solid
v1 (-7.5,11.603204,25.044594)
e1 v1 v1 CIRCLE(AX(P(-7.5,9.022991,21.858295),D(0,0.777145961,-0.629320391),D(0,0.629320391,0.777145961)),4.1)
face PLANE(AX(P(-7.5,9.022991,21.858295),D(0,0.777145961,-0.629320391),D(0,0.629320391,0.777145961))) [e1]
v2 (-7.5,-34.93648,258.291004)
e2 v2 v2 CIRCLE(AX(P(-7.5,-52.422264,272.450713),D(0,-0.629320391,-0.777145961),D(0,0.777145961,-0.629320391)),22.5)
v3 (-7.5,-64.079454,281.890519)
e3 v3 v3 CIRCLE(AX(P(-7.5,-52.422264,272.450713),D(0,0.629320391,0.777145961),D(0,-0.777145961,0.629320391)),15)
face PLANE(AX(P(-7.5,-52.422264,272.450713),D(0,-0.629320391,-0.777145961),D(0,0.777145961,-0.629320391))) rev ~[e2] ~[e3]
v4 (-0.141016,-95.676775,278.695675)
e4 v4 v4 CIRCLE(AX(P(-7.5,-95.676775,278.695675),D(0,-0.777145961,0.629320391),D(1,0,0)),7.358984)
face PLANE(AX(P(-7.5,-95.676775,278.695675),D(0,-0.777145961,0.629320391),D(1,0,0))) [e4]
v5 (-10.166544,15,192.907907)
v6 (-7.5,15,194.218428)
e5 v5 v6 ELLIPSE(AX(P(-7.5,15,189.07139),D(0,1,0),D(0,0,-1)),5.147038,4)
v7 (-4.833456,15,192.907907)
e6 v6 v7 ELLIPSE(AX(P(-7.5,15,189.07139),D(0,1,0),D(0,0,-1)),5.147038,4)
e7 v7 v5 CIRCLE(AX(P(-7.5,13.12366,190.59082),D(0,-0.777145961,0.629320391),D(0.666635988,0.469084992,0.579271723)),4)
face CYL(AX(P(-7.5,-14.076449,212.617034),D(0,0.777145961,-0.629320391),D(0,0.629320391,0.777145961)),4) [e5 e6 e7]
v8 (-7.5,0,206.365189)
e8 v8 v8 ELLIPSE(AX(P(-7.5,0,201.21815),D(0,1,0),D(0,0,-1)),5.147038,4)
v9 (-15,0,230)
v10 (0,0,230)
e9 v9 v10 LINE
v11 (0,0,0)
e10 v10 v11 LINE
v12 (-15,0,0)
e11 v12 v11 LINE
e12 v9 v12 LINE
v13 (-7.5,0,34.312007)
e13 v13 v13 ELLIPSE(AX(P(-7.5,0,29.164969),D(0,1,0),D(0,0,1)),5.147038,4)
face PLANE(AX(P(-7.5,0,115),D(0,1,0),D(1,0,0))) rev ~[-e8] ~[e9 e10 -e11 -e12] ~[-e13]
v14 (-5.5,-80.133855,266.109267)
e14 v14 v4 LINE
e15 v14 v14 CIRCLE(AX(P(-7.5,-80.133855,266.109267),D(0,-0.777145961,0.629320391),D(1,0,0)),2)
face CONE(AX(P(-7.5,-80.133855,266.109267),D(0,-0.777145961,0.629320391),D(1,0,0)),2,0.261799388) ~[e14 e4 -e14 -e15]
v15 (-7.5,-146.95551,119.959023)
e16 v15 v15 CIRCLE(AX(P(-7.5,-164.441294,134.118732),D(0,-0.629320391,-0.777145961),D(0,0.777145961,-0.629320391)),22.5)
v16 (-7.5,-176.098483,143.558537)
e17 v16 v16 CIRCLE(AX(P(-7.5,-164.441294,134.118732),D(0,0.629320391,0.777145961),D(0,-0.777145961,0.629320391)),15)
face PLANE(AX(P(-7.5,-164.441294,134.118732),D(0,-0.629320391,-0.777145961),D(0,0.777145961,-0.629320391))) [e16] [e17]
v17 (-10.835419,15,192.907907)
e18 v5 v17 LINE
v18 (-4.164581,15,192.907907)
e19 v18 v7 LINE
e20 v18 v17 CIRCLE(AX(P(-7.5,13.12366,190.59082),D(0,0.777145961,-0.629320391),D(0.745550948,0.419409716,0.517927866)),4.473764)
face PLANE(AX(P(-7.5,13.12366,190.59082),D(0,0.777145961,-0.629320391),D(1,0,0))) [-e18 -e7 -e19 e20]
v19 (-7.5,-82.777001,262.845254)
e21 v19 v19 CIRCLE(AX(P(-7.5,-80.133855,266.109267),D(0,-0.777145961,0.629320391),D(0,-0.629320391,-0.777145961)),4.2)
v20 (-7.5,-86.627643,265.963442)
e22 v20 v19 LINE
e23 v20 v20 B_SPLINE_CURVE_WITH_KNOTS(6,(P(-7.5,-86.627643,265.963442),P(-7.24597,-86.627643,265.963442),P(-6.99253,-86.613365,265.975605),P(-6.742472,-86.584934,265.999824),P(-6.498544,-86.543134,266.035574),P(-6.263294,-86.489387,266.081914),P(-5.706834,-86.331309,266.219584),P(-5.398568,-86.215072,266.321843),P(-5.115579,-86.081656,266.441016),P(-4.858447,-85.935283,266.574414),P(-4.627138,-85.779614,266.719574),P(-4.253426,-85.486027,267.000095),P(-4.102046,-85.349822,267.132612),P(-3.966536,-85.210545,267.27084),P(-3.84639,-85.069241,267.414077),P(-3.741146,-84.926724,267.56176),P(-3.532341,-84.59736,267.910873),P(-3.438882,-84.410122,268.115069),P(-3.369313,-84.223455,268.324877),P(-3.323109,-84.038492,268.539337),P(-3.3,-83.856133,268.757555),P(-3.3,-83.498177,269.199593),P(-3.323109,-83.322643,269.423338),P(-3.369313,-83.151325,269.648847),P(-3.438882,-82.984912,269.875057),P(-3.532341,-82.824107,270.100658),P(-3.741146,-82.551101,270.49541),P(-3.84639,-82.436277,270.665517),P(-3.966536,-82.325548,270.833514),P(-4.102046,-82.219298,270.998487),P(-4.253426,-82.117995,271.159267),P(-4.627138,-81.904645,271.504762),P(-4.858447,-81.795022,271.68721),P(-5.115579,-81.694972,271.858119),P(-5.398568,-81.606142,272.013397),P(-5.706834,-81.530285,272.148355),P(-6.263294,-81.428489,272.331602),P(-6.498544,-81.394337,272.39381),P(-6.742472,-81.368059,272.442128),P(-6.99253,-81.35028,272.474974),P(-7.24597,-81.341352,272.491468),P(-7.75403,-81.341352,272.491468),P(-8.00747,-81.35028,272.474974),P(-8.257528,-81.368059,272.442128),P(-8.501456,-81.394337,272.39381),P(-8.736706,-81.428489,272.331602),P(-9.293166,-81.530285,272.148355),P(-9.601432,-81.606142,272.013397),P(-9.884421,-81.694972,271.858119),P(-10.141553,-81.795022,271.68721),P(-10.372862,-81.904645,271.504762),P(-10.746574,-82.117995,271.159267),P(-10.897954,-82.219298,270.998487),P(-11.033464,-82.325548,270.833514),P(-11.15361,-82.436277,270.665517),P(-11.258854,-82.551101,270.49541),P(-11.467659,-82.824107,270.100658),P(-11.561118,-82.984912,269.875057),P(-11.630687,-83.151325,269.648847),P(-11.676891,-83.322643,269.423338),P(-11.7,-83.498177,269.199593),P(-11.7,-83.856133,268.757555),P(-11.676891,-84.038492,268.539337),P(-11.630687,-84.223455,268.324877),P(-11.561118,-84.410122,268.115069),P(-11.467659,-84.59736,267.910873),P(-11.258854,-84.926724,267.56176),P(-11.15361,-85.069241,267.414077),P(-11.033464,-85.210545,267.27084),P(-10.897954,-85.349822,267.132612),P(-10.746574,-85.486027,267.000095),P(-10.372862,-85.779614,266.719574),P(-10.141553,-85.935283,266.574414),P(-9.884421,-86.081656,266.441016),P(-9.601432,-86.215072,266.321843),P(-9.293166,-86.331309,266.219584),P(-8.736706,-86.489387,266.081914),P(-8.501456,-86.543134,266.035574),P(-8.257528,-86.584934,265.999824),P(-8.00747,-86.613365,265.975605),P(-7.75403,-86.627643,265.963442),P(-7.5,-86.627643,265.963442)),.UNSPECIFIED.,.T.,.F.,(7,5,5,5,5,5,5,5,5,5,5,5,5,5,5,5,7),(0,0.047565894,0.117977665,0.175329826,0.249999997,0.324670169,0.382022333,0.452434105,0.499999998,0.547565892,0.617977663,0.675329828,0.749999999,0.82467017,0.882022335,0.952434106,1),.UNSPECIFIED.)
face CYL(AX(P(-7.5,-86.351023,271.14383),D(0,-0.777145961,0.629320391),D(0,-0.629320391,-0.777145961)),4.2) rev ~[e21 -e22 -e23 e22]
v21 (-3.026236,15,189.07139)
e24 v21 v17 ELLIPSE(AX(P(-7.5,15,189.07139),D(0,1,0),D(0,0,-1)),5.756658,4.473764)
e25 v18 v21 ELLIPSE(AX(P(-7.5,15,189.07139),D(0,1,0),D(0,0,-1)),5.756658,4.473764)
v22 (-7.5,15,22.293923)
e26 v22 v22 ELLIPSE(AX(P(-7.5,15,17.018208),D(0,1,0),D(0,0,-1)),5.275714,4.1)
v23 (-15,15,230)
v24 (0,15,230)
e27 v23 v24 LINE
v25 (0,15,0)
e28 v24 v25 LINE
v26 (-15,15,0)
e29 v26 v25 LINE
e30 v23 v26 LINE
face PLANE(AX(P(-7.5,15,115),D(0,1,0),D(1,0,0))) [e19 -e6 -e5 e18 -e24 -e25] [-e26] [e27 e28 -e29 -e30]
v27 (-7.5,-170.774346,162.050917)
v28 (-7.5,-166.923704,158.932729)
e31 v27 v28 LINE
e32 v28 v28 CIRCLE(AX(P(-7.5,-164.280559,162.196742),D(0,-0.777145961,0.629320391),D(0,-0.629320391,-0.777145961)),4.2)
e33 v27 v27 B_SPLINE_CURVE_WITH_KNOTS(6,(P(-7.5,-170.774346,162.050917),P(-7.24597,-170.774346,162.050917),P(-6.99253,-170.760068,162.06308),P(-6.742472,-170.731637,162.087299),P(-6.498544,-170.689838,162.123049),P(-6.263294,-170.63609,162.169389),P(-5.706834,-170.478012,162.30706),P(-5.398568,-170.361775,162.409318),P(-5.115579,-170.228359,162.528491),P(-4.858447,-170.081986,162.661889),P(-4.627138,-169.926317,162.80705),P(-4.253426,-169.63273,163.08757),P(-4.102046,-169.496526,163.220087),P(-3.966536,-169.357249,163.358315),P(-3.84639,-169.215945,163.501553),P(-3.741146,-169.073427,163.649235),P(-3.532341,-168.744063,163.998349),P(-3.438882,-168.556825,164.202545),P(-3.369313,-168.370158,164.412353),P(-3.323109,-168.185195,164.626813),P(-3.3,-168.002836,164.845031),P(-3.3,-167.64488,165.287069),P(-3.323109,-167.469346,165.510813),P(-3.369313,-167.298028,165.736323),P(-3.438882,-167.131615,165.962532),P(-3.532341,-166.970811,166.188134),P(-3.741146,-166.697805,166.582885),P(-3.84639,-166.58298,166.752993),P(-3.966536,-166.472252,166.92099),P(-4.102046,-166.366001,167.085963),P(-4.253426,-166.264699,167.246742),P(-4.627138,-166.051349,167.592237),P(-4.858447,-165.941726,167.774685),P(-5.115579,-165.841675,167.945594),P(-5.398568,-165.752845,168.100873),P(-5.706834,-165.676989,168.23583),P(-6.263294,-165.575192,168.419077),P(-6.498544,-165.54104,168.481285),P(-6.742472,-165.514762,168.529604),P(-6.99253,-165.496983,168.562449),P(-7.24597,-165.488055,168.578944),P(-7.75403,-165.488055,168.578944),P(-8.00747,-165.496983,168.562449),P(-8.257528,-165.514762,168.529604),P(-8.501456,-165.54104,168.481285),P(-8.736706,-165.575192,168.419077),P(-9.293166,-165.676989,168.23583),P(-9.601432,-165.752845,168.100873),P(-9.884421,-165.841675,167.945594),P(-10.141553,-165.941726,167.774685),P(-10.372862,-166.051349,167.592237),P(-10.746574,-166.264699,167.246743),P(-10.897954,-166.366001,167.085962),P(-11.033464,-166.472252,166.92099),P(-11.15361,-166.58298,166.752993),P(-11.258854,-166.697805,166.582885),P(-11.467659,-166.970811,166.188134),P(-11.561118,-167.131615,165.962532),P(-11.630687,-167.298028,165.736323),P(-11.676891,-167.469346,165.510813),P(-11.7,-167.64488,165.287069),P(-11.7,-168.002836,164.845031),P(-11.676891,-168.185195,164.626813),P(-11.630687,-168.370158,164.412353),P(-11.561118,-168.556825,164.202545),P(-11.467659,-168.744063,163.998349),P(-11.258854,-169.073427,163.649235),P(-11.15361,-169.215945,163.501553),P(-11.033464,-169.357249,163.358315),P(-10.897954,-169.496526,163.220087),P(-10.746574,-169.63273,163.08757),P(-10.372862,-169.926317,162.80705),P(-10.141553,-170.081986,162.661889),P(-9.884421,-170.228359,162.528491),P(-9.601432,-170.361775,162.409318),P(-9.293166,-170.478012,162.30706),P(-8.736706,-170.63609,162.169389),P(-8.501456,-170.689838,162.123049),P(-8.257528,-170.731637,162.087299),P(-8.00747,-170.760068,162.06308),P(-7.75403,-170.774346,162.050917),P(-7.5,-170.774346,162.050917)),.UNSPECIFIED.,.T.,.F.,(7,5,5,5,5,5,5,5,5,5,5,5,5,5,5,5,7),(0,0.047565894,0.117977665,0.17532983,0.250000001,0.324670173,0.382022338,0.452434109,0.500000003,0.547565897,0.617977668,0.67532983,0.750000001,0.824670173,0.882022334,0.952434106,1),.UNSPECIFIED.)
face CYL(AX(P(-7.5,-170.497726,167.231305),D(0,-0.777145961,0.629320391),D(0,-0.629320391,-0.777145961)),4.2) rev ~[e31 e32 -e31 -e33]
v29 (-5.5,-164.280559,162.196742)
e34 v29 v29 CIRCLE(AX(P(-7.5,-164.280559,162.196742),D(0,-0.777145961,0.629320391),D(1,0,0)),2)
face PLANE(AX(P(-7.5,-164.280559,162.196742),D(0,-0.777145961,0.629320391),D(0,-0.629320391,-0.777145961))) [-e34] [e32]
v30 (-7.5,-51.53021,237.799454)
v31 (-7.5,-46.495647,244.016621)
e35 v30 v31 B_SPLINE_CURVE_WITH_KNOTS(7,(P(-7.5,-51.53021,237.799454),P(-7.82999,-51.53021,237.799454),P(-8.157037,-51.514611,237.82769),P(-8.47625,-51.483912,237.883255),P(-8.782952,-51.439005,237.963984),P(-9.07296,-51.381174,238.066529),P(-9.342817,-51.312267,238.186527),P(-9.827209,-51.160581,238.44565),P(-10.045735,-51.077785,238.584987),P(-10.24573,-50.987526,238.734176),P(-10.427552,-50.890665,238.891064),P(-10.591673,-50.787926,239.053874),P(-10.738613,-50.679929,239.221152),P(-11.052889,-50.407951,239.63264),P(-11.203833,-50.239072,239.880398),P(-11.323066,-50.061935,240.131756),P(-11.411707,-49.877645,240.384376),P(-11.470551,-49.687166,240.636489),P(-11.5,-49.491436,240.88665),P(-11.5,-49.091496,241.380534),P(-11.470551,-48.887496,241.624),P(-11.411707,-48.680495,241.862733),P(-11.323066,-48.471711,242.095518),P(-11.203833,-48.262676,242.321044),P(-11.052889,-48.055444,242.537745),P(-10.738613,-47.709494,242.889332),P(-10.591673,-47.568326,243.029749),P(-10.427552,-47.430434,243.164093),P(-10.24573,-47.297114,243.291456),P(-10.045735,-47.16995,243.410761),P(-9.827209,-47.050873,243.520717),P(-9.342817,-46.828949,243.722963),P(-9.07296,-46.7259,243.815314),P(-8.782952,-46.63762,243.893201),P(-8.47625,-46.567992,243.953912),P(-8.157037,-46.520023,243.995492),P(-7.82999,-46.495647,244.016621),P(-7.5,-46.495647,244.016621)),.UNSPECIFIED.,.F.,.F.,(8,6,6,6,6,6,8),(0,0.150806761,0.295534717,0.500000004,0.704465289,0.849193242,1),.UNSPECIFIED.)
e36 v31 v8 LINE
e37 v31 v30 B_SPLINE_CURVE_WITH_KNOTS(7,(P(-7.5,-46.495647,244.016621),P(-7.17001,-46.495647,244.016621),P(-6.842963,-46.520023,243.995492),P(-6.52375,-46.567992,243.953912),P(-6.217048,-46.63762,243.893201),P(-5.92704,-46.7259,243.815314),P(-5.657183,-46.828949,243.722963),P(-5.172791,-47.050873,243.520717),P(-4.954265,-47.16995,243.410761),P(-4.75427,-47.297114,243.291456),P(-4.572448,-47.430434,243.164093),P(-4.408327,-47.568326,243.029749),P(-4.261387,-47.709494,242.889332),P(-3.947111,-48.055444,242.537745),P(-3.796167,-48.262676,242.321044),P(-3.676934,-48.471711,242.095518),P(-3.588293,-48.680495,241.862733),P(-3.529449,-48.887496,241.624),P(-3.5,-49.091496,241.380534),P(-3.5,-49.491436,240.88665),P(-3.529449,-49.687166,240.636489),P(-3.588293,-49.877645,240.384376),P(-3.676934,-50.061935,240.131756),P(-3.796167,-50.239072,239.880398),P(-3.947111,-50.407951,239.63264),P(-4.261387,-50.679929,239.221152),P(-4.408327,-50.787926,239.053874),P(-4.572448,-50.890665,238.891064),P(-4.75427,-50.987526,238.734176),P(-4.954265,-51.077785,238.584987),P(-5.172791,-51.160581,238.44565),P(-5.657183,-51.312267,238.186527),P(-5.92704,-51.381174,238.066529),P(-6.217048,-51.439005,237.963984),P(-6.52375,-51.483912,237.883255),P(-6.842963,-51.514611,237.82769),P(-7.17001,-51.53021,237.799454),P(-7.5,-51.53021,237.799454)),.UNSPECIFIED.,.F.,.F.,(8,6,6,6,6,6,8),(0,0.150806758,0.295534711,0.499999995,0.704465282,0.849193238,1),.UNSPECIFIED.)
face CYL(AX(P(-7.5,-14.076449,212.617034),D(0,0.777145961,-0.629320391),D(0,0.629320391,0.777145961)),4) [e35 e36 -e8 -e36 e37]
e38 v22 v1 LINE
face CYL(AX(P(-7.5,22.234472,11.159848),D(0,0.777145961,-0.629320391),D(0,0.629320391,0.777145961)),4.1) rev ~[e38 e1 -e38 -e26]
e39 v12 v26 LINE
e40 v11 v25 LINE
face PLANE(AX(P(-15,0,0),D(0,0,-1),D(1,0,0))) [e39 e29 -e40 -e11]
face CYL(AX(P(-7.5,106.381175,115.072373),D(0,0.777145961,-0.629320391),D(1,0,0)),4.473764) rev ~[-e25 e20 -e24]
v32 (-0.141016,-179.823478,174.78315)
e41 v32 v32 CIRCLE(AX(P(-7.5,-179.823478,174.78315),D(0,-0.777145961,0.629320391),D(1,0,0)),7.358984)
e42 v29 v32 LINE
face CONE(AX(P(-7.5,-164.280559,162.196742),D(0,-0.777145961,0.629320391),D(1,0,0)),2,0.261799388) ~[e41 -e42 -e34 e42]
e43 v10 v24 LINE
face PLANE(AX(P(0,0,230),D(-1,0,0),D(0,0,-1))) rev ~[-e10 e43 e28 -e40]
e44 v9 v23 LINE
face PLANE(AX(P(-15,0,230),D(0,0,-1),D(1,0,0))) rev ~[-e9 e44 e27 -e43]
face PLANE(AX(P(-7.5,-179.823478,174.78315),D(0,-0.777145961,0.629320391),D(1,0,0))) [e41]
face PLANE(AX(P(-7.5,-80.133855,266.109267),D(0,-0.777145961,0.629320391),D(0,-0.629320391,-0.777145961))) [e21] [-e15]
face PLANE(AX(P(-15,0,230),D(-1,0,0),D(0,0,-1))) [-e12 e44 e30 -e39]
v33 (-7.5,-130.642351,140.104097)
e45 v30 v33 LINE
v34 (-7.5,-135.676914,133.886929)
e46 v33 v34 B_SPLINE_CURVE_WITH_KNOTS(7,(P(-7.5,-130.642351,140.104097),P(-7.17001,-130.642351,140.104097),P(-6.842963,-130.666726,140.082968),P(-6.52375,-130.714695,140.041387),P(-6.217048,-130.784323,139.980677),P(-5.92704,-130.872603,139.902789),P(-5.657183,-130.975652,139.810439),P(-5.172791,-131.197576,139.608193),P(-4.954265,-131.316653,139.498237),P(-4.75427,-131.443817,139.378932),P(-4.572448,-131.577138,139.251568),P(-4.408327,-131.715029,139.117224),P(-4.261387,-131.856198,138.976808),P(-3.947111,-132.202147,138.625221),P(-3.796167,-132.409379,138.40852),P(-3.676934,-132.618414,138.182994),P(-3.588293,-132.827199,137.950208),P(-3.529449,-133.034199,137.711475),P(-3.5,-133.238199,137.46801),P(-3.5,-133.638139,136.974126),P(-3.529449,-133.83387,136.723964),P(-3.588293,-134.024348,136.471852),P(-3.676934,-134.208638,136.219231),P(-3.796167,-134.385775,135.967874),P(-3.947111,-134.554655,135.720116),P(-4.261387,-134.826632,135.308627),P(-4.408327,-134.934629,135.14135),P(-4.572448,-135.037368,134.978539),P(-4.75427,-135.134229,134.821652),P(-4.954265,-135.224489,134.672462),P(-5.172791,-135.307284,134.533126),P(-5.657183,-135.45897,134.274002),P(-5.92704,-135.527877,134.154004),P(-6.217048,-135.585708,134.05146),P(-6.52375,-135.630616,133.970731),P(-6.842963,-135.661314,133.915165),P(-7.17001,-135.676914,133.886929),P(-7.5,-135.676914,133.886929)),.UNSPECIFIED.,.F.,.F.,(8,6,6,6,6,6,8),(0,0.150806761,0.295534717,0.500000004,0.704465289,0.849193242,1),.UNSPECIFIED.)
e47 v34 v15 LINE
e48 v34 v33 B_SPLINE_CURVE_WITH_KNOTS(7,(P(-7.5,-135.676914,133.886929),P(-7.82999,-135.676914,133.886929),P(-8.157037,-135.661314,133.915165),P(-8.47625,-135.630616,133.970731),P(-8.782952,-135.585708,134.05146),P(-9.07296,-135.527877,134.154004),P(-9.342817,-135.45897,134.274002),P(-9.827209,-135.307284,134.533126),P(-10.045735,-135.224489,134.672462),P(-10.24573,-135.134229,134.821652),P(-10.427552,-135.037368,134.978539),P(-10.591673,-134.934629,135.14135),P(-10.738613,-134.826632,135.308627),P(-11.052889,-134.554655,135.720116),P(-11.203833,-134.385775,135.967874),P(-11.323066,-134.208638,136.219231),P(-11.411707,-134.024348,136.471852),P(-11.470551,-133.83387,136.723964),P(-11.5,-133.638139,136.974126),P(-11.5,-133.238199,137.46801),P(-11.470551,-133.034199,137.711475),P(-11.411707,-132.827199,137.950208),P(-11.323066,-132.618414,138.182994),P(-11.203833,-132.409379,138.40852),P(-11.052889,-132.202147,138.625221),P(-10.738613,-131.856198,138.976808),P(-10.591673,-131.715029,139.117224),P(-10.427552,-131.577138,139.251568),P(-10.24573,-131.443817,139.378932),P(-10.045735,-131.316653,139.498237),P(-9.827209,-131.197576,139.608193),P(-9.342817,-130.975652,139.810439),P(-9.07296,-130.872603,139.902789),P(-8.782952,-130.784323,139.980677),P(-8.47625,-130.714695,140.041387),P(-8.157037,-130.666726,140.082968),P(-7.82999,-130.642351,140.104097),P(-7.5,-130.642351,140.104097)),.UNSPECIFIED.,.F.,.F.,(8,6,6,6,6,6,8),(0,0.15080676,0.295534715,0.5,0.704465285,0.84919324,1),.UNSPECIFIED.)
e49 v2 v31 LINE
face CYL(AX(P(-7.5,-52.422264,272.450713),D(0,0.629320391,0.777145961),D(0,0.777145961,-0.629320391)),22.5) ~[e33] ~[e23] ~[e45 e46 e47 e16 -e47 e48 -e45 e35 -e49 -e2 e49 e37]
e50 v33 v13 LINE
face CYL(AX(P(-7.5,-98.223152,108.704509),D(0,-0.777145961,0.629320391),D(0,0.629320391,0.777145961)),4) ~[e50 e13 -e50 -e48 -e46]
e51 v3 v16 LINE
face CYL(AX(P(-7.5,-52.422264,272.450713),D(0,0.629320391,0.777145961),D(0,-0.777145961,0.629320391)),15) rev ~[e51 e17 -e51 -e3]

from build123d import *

# Parameters (mm, degrees)
SKETCH2_W                     = 15
SKETCH2_H                     = 230
BOSS_EXTRUDE2_DEPTH           = 15
SKETCH4_R                     = 4
BOSS_EXTRUDE3_DEPTH           = 155
SKETCH5_R                     = 4.473763718
CUT_EXTRUDE1_DEPTH            = 120
SKETCH6_R                     = 4.1
CUT_EXTRUDE2_DEPTH            = 17
SKETCH7_R                     = 5.311376806
SKETCH7_R_2                   = 5.6699774
CUT_EXTRUDE3_DEPTH            = 62
SKETCH8_R                     = 22.5
BOSS_EXTRUDE4_DEPTH           = 178
SKETCH9_R                     = 4.2
CUT_EXTRUDE4_DEPTH            = 8
SKETCH10_R                    = 2
BOSS_EXTRUDE5_DEPTH           = 20
BOSS_EXTRUDE5_DRAFT           = -15
BOSS_EXTRUDE5_PROFILE_2_DEPTH = 20
BOSS_EXTRUDE5_PROFILE_2_DRAFT = -15
SKETCH11_R                    = 15
CUT_EXTRUDE5_DEPTH            = 193


with BuildPart() as part:
    # Sketch2 → Boss-Extrude2 (new body)
    with BuildSketch(Plane(origin=(0, 0, 0), x_dir=(1, 0, 0), z_dir=(0, 1, 0))):
        with Locations((-7.5, -115)):
            Rectangle(SKETCH2_W, SKETCH2_H)
    extrude(amount=BOSS_EXTRUDE2_DEPTH)

    # Sketch4 → Boss-Extrude3 (add, symmetric)
    with BuildSketch(Plane(origin=(0, -112.486974084, 91.090155556), x_dir=(1, 0, 0), z_dir=(0, 0.7771459614569742, -0.6293203910498333))):
        with Locations(Location((-7.5, -22.665437835, 0), (0, 0, 270))):
            Circle(SKETCH4_R)
        with Locations(Location((-7.5, -156.375872868, 0), (0, 0, 270))):
            Circle(SKETCH4_R)
    extrude(amount=BOSS_EXTRUDE3_DEPTH, both=True)

    # Sketch5 → Cut-Extrude1 (cut)
    with BuildSketch(Plane(origin=(0, 7.970649941, -6.454505057), x_dir=(1, 0, 0), z_dir=(0, 0.7771459614569743, -0.6293203910498333))):
        with Locations((-7.5, -156.375872868)):
            Circle(SKETCH5_R)
    extrude(amount=-CUT_EXTRUDE1_DEPTH, mode=Mode.SUBTRACT)

    # Sketch6 → Cut-Extrude2 (cut)
    with BuildSketch(Plane(origin=(0, 7.970649941, -6.454505057), x_dir=(1, 0, 0), z_dir=(0, 0.7771459614569743, -0.6293203910498333))):
        with Locations(Location((-7.5, -22.665437835, 0), (0, 0, 270))):
            Circle(SKETCH6_R)
    extrude(amount=-CUT_EXTRUDE2_DEPTH, mode=Mode.SUBTRACT)

    # Sketch7 → Cut-Extrude3 (cut)
    with BuildSketch(Plane(origin=(0, -232.94459811, 188.634816169), x_dir=(1, 0, 0), z_dir=(0, -0.7771459614569743, 0.6293203910498333))):
        with Locations((-7.5, 22.665437835)):
            Circle(SKETCH7_R)
        with Locations((-7.5, 156.375872868)):
            Circle(SKETCH7_R_2)
    extrude(amount=-CUT_EXTRUDE3_DEPTH, mode=Mode.SUBTRACT)

    # Sketch8 → Boss-Extrude4 (add)
    with BuildSketch(Plane(origin=(0, 112.486974084, 138.909844444), x_dir=(1, 0, 0), z_dir=(0, -0.6293203910498333, -0.7771459614569743))):
        with Locations(Location((-7.5, 212.198540139, 0), (0, 0, 270))):
            Circle(SKETCH8_R)
    extrude(amount=BOSS_EXTRUDE4_DEPTH)

    # Sketch9 → Cut-Extrude4 (cut)
    with BuildSketch(Plane(origin=(0, -184.7615485, 149.616951924), x_dir=(1, 0, 0), z_dir=(0, -0.7771459614569743, 0.6293203910498334))):
        with Locations(Location((-7.5, 156.375872868, 0), (0, 0, 270))):
            Circle(SKETCH9_R)
        with Locations(Location((-7.5, 22.665437835, 0), (0, 0, 270))):
            Circle(SKETCH9_R)
    extrude(amount=-CUT_EXTRUDE4_DEPTH, mode=Mode.SUBTRACT)


with BuildPart() as boss_extrude5_tool:
    # Sketch10 → Boss-Extrude5 (with draft: the straight prism first)
    with BuildSketch(Plane(origin=(0, -178.544380808, 144.582388795), x_dir=(1, 0, 0), z_dir=(0, -0.777145961456974, 0.6293203910498335))):
        with Locations((-7.5, 156.375872868)):
            Circle(SKETCH10_R)
    extrude(amount=BOSS_EXTRUDE5_DEPTH)
    # Boss-Extrude5: the draft: its side faces are tilted about the plane it starts from
    boss_extrude5_sides = [boss_extrude5_tool.faces().sort_by_distance(p)[0] for p in [
        (-9.5, -87.905314959, 272.402470774),
    ]]
    draft(boss_extrude5_sides, Plane(origin=(0, -178.544380808, 144.582388795), x_dir=(1, 0, 0), z_dir=(0, -0.777145961456974, 0.6293203910498335)), BOSS_EXTRUDE5_DRAFT)


with BuildPart() as part_1:
    add(part.part)

    # Boss-Extrude5: add boss_extrude5_tool
    add(boss_extrude5_tool.part)


with BuildPart() as boss_extrude5_profile_2_tool:
    # Sketch10 → Boss-Extrude5 profile 2 (with draft: the straight prism first)
    with BuildSketch(Plane(origin=(0, -178.544380808, 144.582388795), x_dir=(1, 0, 0), z_dir=(0, -0.777145961456974, 0.6293203910498335))):
        with Locations((-7.5, 22.665437835)):
            Circle(SKETCH10_R)
    extrude(amount=BOSS_EXTRUDE5_PROFILE_2_DEPTH)
    # Boss-Extrude5 profile 2: the draft: its side faces are tilted about the plane it starts from
    boss_extrude5_profile_2_sides = [boss_extrude5_profile_2_tool.faces().sort_by_distance(p)[0] for p in [
        (-9.5, -172.052018221, 168.489946184),
    ]]
    draft(boss_extrude5_profile_2_sides, Plane(origin=(0, -178.544380808, 144.582388795), x_dir=(1, 0, 0), z_dir=(0, -0.777145961456974, 0.6293203910498335)), BOSS_EXTRUDE5_PROFILE_2_DRAFT)


with BuildPart() as part_2:
    add(part_1.part)

    # Boss-Extrude5 profile 2: add boss_extrude5_profile_2_tool
    add(boss_extrude5_profile_2_tool.part)

    # Sketch11 → Cut-Extrude5 (cut)
    with BuildSketch(Plane(origin=(0, 112.486974084, 138.909844444), x_dir=(1, 0, 0), z_dir=(0, 0.6293203910498334, 0.7771459614569743))):
        with Locations(Location((-7.5, -212.198540139, 0), (0, 0, 270))):
            Circle(SKETCH11_R)
    extrude(amount=-CUT_EXTRUDE5_DEPTH, mode=Mode.SUBTRACT)


solid = part_2.part
